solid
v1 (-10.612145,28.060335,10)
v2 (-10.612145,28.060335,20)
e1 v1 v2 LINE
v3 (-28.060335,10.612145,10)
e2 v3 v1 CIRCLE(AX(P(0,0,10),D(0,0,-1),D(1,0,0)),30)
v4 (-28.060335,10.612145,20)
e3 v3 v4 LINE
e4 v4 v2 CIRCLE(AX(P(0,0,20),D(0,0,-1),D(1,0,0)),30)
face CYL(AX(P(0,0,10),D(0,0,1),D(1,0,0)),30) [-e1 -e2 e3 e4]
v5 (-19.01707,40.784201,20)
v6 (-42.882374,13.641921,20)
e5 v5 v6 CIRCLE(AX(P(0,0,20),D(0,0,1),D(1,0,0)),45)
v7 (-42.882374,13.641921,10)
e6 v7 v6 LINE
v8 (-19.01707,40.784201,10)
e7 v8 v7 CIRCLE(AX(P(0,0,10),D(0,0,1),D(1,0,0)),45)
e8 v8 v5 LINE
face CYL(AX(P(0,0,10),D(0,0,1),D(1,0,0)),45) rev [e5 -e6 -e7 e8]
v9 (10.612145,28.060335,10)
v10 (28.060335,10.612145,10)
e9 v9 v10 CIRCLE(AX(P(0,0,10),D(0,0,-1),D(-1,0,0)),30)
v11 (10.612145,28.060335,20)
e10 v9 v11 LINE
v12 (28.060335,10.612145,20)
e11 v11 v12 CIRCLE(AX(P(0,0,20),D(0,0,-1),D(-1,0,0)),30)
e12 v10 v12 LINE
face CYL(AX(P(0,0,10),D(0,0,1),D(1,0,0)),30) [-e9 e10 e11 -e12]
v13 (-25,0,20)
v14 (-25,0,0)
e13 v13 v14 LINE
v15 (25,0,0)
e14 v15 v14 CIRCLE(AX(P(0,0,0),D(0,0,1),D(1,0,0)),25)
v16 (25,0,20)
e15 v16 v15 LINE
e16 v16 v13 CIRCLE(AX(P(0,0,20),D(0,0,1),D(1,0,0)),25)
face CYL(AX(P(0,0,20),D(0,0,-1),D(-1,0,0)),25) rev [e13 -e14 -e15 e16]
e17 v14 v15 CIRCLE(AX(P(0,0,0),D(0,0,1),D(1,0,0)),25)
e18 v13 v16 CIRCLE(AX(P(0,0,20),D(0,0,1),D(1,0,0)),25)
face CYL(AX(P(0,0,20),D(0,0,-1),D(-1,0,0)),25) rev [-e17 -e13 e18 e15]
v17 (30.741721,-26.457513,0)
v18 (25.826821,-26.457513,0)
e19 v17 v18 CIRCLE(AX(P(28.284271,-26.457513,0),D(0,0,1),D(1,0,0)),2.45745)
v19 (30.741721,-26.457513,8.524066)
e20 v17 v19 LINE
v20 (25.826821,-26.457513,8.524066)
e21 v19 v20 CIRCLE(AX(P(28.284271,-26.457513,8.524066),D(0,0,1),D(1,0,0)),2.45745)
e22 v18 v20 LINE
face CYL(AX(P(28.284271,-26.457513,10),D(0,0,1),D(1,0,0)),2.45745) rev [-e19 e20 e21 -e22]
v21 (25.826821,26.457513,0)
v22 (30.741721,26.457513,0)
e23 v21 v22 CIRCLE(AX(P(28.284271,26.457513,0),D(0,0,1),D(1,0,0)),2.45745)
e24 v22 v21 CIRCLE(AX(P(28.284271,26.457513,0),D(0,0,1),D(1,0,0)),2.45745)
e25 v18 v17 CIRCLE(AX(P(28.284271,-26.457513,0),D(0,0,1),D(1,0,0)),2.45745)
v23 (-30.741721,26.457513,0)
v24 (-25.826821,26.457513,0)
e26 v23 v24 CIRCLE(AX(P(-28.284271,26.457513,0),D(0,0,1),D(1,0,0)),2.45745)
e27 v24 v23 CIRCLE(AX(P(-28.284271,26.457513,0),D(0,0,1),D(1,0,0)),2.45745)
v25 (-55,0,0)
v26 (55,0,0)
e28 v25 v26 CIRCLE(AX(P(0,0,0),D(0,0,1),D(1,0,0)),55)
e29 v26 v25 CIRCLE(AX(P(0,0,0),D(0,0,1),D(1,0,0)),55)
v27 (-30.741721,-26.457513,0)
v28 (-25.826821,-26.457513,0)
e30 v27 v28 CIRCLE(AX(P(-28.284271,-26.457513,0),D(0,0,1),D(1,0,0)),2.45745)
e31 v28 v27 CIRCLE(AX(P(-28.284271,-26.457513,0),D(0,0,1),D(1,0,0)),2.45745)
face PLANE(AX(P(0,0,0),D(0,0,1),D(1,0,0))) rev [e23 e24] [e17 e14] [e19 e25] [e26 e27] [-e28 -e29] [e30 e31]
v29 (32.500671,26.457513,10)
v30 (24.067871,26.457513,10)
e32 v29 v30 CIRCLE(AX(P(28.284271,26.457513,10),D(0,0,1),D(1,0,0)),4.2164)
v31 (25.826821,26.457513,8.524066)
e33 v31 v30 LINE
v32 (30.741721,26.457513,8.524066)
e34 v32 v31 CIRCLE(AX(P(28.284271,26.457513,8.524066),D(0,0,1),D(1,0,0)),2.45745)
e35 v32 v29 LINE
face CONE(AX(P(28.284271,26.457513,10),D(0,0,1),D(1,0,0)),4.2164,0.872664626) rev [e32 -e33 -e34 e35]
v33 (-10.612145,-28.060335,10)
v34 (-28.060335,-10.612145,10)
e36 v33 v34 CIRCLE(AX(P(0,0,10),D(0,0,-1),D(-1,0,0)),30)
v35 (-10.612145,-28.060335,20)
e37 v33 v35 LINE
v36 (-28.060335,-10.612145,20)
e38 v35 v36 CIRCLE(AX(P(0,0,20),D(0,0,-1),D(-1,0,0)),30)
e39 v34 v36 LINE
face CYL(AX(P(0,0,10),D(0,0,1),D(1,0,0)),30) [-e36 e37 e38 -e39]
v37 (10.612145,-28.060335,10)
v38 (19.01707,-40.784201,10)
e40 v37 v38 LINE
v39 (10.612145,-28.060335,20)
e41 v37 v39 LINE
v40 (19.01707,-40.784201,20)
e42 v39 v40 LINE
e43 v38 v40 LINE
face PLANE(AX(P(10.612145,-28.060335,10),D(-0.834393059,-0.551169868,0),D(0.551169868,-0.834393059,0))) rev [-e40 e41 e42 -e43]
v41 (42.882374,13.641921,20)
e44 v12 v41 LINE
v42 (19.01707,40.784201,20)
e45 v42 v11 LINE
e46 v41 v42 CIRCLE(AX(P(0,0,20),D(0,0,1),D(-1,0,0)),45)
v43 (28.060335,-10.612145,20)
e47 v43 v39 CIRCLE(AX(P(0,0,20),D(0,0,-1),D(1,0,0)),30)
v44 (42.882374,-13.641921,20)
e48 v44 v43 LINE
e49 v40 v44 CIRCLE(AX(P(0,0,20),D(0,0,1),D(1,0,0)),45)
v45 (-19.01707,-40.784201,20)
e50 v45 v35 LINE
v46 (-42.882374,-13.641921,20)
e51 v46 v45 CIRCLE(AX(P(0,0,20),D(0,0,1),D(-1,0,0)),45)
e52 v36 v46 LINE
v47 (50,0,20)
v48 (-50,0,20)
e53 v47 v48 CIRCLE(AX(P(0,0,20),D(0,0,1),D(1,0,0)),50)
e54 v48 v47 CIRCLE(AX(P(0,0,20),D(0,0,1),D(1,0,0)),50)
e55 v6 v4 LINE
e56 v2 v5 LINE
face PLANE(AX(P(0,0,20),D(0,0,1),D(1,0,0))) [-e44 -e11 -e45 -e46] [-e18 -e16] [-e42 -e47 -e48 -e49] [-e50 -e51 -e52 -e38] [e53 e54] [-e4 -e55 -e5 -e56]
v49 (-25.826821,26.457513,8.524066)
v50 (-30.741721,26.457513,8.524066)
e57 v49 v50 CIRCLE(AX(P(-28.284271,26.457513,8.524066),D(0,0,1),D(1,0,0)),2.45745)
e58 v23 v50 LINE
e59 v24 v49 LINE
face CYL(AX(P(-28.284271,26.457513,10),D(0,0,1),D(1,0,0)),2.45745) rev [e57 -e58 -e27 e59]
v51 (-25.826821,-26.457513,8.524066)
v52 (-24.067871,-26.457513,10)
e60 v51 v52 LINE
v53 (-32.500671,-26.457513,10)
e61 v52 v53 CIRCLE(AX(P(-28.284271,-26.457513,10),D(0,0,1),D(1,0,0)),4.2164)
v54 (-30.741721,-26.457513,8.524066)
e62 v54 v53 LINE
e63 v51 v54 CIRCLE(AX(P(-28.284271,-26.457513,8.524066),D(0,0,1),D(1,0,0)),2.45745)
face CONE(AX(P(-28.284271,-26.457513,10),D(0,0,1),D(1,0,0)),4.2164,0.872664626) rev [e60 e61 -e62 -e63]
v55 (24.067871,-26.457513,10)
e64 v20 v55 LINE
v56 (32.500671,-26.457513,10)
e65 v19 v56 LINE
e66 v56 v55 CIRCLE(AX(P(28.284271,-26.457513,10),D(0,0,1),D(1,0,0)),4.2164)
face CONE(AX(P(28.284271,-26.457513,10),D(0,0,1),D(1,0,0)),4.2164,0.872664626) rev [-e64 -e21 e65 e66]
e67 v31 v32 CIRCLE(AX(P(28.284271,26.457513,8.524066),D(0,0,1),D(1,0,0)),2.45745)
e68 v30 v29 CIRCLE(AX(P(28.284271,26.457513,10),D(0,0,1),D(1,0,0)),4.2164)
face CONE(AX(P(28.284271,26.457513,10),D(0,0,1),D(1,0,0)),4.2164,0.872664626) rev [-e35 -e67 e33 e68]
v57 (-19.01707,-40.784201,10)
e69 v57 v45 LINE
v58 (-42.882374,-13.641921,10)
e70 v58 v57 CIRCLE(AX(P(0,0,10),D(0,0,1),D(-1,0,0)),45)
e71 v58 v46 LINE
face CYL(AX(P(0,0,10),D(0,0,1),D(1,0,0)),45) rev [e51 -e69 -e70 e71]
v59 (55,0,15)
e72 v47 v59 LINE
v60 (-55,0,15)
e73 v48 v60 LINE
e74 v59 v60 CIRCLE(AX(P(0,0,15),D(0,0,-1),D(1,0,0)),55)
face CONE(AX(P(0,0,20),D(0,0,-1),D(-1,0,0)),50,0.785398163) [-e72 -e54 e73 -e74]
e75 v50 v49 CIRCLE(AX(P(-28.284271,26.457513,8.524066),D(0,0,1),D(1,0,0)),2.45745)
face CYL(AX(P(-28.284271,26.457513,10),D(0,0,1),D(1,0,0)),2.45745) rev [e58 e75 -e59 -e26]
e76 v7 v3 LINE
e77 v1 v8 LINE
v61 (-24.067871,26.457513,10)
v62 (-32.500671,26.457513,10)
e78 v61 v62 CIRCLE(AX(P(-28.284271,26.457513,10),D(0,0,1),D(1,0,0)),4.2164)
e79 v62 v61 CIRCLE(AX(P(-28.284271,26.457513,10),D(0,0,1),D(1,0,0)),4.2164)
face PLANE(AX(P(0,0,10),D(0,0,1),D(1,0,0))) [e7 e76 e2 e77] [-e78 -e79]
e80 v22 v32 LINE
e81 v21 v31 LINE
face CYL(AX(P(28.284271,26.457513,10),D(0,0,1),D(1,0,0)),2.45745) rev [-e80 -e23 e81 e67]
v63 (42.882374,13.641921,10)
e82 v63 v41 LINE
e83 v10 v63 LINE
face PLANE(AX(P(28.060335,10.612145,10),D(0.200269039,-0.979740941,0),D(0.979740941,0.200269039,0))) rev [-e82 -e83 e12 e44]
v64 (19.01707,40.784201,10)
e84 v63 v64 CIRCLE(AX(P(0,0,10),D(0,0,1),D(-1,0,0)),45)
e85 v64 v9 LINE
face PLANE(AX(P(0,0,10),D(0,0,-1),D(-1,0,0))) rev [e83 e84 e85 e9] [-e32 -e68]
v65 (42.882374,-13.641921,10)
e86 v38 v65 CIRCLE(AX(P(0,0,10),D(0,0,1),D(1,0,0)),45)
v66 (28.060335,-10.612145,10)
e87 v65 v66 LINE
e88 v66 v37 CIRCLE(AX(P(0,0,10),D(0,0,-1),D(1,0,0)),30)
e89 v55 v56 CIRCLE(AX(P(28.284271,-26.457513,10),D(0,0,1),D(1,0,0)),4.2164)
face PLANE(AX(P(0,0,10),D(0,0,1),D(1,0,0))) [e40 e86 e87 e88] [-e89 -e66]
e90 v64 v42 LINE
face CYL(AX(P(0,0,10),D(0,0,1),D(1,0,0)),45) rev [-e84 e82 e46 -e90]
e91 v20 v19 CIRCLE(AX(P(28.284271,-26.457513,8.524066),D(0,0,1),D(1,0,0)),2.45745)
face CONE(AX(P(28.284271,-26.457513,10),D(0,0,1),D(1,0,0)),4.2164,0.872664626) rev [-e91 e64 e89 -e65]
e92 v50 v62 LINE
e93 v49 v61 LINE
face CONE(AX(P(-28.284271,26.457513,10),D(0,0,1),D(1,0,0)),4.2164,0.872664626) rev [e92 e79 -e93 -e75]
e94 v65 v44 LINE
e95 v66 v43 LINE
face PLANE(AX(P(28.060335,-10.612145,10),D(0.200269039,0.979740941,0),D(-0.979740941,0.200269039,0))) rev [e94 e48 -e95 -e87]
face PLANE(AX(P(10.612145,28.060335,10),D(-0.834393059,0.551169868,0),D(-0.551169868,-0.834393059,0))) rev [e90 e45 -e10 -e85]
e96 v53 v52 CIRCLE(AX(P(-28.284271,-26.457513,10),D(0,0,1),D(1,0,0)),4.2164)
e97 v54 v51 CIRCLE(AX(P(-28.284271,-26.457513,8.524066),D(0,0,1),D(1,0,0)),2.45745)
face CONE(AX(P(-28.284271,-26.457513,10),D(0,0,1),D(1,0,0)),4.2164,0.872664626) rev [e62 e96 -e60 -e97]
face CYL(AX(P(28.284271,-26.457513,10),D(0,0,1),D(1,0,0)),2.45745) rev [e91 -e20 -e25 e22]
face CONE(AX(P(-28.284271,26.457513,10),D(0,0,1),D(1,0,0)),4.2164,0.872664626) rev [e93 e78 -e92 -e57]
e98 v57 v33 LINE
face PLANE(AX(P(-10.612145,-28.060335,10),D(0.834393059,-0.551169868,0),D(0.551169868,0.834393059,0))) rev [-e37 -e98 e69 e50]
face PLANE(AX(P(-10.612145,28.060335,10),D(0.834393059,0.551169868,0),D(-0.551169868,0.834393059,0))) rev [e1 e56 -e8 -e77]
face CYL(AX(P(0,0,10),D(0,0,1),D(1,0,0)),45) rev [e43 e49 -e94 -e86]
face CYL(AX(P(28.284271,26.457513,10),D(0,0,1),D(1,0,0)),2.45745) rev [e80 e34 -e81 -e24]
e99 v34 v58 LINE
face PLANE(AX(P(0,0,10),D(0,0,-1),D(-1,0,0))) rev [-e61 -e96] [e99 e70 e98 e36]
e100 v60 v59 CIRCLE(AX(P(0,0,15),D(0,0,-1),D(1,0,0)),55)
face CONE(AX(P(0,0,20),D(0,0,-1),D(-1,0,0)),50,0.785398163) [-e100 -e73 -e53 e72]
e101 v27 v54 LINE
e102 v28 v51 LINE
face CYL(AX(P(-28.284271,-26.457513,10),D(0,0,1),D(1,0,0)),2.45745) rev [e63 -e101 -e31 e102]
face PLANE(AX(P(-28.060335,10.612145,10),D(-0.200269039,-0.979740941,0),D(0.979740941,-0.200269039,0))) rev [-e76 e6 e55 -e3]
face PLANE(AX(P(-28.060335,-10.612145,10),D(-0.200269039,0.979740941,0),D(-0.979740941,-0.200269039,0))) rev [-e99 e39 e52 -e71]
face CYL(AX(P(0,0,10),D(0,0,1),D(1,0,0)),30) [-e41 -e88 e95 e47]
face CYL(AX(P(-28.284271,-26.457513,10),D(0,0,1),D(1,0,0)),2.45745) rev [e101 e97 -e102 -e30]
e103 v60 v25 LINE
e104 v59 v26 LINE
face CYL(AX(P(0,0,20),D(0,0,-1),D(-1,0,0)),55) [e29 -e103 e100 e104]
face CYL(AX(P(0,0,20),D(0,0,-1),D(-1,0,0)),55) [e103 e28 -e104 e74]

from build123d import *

# Parameters (mm, degrees)
SKETCH1_R                                         = 55
SKETCH1_R_2                                       = 25
BOSS_EXTRUDE1_DEPTH                               = 20
CUT_EXTRUDE1_DEPTH                                = 10
CHAMFER1_SIZE                                     = 5
CSK_FOR_8_FLAT_HEAD_MACHINE_SCREW_100_D           = 4.9149
CSK_FOR_8_FLAT_HEAD_MACHINE_SCREW_100_CSINK_D     = 8.4328
CSK_FOR_8_FLAT_HEAD_MACHINE_SCREW_100_CSINK_ANGLE = 100
MIRROR2_COPY_1_D                                  = 4.9149
MIRROR2_COPY_1_CSINK_D                            = 8.4328
MIRROR2_COPY_1_CSINK_ANGLE                        = 100


with BuildPart() as part:
    # Sketch1 → Boss-Extrude1 (new body)
    with BuildSketch(Plane.XY):
        Circle(SKETCH1_R)
        Circle(SKETCH1_R_2, mode=Mode.SUBTRACT)
    extrude(amount=BOSS_EXTRUDE1_DEPTH)

    # Sketch2 → Cut-Extrude1 (cut)
    with BuildSketch(Plane.XY.offset(20)):
        with BuildLine():
            Line((-10.612144625, 28.060334753), (-19.017070243, 40.784200855))
            ThreePointArc((-19.017070243, 40.784200855), (-33.794395167, 29.714287056), (-42.88237403, 13.641920597))
            Line((-42.88237403, 13.641920597), (-28.060334753, 10.612144625))
            ThreePointArc((-28.060334753, 10.612144625), (-21.213203436, 21.213203436), (-10.612144625, 28.060334753))
        make_face()
        with BuildLine():
            Line((28.060334753, 10.612144625), (42.88237403, 13.641920597))
            ThreePointArc((42.88237403, 13.641920597), (33.794395167, 29.714287056), (19.017070243, 40.784200855))
            Line((19.017070243, 40.784200855), (10.612144625, 28.060334753))
            ThreePointArc((10.612144625, 28.060334753), (21.213203436, 21.213203436), (28.060334753, 10.612144625))
        make_face()
        with BuildLine():
            Line((10.612144625, -28.060334753), (19.017070243, -40.784200855))
            ThreePointArc((19.017070243, -40.784200855), (33.794395167, -29.714287056), (42.88237403, -13.641920597))
            Line((42.88237403, -13.641920597), (28.060334753, -10.612144625))
            ThreePointArc((28.060334753, -10.612144625), (21.213203436, -21.213203436), (10.612144625, -28.060334753))
        make_face()
        with BuildLine():
            Line((-28.060334753, -10.612144625), (-42.88237403, -13.641920597))
            ThreePointArc((-42.88237403, -13.641920597), (-33.794395167, -29.714287056), (-19.017070243, -40.784200855))
            Line((-19.017070243, -40.784200855), (-10.612144625, -28.060334753))
            ThreePointArc((-10.612144625, -28.060334753), (-21.213203436, -21.213203436), (-28.060334753, -10.612144625))
        make_face()
    extrude(amount=-CUT_EXTRUDE1_DEPTH, mode=Mode.SUBTRACT)

    # Chamfer1
    chamfer1_edges = [part.edges().sort_by_distance(p)[0] for p in [
        (-55, 0, 20),
    ]]
    chamfer(chamfer1_edges, length=CHAMFER1_SIZE)

    # CSK for #8 Flat Head Machine Screw (100)1 (through all)
    with Locations(Plane(origin=(-28.284271247, 26.457513111, 10), x_dir=(1, 0, 0), z_dir=(0, 0, 1))):
        with Locations((0, 0)):
            csk_for_8_flat_head_machine_screw_100 = CounterSinkHole(CSK_FOR_8_FLAT_HEAD_MACHINE_SCREW_100_D / 2, CSK_FOR_8_FLAT_HEAD_MACHINE_SCREW_100_CSINK_D / 2, counter_sink_angle=CSK_FOR_8_FLAT_HEAD_MACHINE_SCREW_100_CSINK_ANGLE)

    # Mirror1: CSK for #8 Flat Head Machine Screw (100)1 across plane
    add(csk_for_8_flat_head_machine_screw_100.mirror(Plane(origin=(0, 0, 0), x_dir=(0, 0, 1), z_dir=(1, 0, 0))), mode=Mode.SUBTRACT)

    # Mirror2: CSK for #8 Flat Head Machine Screw (100)1 across plane
    add(csk_for_8_flat_head_machine_screw_100.mirror(Plane.ZX), mode=Mode.SUBTRACT)

    # Mirror2 copy 1 (through all)
    with Locations(Plane(origin=(28.284271247, -26.457513111, 10), x_dir=(-1, 0, 0), z_dir=(0, 0, 1))):
        with Locations((0, 0)):
            CounterSinkHole(MIRROR2_COPY_1_D / 2, MIRROR2_COPY_1_CSINK_D / 2, counter_sink_angle=MIRROR2_COPY_1_CSINK_ANGLE)


solid = part.part
